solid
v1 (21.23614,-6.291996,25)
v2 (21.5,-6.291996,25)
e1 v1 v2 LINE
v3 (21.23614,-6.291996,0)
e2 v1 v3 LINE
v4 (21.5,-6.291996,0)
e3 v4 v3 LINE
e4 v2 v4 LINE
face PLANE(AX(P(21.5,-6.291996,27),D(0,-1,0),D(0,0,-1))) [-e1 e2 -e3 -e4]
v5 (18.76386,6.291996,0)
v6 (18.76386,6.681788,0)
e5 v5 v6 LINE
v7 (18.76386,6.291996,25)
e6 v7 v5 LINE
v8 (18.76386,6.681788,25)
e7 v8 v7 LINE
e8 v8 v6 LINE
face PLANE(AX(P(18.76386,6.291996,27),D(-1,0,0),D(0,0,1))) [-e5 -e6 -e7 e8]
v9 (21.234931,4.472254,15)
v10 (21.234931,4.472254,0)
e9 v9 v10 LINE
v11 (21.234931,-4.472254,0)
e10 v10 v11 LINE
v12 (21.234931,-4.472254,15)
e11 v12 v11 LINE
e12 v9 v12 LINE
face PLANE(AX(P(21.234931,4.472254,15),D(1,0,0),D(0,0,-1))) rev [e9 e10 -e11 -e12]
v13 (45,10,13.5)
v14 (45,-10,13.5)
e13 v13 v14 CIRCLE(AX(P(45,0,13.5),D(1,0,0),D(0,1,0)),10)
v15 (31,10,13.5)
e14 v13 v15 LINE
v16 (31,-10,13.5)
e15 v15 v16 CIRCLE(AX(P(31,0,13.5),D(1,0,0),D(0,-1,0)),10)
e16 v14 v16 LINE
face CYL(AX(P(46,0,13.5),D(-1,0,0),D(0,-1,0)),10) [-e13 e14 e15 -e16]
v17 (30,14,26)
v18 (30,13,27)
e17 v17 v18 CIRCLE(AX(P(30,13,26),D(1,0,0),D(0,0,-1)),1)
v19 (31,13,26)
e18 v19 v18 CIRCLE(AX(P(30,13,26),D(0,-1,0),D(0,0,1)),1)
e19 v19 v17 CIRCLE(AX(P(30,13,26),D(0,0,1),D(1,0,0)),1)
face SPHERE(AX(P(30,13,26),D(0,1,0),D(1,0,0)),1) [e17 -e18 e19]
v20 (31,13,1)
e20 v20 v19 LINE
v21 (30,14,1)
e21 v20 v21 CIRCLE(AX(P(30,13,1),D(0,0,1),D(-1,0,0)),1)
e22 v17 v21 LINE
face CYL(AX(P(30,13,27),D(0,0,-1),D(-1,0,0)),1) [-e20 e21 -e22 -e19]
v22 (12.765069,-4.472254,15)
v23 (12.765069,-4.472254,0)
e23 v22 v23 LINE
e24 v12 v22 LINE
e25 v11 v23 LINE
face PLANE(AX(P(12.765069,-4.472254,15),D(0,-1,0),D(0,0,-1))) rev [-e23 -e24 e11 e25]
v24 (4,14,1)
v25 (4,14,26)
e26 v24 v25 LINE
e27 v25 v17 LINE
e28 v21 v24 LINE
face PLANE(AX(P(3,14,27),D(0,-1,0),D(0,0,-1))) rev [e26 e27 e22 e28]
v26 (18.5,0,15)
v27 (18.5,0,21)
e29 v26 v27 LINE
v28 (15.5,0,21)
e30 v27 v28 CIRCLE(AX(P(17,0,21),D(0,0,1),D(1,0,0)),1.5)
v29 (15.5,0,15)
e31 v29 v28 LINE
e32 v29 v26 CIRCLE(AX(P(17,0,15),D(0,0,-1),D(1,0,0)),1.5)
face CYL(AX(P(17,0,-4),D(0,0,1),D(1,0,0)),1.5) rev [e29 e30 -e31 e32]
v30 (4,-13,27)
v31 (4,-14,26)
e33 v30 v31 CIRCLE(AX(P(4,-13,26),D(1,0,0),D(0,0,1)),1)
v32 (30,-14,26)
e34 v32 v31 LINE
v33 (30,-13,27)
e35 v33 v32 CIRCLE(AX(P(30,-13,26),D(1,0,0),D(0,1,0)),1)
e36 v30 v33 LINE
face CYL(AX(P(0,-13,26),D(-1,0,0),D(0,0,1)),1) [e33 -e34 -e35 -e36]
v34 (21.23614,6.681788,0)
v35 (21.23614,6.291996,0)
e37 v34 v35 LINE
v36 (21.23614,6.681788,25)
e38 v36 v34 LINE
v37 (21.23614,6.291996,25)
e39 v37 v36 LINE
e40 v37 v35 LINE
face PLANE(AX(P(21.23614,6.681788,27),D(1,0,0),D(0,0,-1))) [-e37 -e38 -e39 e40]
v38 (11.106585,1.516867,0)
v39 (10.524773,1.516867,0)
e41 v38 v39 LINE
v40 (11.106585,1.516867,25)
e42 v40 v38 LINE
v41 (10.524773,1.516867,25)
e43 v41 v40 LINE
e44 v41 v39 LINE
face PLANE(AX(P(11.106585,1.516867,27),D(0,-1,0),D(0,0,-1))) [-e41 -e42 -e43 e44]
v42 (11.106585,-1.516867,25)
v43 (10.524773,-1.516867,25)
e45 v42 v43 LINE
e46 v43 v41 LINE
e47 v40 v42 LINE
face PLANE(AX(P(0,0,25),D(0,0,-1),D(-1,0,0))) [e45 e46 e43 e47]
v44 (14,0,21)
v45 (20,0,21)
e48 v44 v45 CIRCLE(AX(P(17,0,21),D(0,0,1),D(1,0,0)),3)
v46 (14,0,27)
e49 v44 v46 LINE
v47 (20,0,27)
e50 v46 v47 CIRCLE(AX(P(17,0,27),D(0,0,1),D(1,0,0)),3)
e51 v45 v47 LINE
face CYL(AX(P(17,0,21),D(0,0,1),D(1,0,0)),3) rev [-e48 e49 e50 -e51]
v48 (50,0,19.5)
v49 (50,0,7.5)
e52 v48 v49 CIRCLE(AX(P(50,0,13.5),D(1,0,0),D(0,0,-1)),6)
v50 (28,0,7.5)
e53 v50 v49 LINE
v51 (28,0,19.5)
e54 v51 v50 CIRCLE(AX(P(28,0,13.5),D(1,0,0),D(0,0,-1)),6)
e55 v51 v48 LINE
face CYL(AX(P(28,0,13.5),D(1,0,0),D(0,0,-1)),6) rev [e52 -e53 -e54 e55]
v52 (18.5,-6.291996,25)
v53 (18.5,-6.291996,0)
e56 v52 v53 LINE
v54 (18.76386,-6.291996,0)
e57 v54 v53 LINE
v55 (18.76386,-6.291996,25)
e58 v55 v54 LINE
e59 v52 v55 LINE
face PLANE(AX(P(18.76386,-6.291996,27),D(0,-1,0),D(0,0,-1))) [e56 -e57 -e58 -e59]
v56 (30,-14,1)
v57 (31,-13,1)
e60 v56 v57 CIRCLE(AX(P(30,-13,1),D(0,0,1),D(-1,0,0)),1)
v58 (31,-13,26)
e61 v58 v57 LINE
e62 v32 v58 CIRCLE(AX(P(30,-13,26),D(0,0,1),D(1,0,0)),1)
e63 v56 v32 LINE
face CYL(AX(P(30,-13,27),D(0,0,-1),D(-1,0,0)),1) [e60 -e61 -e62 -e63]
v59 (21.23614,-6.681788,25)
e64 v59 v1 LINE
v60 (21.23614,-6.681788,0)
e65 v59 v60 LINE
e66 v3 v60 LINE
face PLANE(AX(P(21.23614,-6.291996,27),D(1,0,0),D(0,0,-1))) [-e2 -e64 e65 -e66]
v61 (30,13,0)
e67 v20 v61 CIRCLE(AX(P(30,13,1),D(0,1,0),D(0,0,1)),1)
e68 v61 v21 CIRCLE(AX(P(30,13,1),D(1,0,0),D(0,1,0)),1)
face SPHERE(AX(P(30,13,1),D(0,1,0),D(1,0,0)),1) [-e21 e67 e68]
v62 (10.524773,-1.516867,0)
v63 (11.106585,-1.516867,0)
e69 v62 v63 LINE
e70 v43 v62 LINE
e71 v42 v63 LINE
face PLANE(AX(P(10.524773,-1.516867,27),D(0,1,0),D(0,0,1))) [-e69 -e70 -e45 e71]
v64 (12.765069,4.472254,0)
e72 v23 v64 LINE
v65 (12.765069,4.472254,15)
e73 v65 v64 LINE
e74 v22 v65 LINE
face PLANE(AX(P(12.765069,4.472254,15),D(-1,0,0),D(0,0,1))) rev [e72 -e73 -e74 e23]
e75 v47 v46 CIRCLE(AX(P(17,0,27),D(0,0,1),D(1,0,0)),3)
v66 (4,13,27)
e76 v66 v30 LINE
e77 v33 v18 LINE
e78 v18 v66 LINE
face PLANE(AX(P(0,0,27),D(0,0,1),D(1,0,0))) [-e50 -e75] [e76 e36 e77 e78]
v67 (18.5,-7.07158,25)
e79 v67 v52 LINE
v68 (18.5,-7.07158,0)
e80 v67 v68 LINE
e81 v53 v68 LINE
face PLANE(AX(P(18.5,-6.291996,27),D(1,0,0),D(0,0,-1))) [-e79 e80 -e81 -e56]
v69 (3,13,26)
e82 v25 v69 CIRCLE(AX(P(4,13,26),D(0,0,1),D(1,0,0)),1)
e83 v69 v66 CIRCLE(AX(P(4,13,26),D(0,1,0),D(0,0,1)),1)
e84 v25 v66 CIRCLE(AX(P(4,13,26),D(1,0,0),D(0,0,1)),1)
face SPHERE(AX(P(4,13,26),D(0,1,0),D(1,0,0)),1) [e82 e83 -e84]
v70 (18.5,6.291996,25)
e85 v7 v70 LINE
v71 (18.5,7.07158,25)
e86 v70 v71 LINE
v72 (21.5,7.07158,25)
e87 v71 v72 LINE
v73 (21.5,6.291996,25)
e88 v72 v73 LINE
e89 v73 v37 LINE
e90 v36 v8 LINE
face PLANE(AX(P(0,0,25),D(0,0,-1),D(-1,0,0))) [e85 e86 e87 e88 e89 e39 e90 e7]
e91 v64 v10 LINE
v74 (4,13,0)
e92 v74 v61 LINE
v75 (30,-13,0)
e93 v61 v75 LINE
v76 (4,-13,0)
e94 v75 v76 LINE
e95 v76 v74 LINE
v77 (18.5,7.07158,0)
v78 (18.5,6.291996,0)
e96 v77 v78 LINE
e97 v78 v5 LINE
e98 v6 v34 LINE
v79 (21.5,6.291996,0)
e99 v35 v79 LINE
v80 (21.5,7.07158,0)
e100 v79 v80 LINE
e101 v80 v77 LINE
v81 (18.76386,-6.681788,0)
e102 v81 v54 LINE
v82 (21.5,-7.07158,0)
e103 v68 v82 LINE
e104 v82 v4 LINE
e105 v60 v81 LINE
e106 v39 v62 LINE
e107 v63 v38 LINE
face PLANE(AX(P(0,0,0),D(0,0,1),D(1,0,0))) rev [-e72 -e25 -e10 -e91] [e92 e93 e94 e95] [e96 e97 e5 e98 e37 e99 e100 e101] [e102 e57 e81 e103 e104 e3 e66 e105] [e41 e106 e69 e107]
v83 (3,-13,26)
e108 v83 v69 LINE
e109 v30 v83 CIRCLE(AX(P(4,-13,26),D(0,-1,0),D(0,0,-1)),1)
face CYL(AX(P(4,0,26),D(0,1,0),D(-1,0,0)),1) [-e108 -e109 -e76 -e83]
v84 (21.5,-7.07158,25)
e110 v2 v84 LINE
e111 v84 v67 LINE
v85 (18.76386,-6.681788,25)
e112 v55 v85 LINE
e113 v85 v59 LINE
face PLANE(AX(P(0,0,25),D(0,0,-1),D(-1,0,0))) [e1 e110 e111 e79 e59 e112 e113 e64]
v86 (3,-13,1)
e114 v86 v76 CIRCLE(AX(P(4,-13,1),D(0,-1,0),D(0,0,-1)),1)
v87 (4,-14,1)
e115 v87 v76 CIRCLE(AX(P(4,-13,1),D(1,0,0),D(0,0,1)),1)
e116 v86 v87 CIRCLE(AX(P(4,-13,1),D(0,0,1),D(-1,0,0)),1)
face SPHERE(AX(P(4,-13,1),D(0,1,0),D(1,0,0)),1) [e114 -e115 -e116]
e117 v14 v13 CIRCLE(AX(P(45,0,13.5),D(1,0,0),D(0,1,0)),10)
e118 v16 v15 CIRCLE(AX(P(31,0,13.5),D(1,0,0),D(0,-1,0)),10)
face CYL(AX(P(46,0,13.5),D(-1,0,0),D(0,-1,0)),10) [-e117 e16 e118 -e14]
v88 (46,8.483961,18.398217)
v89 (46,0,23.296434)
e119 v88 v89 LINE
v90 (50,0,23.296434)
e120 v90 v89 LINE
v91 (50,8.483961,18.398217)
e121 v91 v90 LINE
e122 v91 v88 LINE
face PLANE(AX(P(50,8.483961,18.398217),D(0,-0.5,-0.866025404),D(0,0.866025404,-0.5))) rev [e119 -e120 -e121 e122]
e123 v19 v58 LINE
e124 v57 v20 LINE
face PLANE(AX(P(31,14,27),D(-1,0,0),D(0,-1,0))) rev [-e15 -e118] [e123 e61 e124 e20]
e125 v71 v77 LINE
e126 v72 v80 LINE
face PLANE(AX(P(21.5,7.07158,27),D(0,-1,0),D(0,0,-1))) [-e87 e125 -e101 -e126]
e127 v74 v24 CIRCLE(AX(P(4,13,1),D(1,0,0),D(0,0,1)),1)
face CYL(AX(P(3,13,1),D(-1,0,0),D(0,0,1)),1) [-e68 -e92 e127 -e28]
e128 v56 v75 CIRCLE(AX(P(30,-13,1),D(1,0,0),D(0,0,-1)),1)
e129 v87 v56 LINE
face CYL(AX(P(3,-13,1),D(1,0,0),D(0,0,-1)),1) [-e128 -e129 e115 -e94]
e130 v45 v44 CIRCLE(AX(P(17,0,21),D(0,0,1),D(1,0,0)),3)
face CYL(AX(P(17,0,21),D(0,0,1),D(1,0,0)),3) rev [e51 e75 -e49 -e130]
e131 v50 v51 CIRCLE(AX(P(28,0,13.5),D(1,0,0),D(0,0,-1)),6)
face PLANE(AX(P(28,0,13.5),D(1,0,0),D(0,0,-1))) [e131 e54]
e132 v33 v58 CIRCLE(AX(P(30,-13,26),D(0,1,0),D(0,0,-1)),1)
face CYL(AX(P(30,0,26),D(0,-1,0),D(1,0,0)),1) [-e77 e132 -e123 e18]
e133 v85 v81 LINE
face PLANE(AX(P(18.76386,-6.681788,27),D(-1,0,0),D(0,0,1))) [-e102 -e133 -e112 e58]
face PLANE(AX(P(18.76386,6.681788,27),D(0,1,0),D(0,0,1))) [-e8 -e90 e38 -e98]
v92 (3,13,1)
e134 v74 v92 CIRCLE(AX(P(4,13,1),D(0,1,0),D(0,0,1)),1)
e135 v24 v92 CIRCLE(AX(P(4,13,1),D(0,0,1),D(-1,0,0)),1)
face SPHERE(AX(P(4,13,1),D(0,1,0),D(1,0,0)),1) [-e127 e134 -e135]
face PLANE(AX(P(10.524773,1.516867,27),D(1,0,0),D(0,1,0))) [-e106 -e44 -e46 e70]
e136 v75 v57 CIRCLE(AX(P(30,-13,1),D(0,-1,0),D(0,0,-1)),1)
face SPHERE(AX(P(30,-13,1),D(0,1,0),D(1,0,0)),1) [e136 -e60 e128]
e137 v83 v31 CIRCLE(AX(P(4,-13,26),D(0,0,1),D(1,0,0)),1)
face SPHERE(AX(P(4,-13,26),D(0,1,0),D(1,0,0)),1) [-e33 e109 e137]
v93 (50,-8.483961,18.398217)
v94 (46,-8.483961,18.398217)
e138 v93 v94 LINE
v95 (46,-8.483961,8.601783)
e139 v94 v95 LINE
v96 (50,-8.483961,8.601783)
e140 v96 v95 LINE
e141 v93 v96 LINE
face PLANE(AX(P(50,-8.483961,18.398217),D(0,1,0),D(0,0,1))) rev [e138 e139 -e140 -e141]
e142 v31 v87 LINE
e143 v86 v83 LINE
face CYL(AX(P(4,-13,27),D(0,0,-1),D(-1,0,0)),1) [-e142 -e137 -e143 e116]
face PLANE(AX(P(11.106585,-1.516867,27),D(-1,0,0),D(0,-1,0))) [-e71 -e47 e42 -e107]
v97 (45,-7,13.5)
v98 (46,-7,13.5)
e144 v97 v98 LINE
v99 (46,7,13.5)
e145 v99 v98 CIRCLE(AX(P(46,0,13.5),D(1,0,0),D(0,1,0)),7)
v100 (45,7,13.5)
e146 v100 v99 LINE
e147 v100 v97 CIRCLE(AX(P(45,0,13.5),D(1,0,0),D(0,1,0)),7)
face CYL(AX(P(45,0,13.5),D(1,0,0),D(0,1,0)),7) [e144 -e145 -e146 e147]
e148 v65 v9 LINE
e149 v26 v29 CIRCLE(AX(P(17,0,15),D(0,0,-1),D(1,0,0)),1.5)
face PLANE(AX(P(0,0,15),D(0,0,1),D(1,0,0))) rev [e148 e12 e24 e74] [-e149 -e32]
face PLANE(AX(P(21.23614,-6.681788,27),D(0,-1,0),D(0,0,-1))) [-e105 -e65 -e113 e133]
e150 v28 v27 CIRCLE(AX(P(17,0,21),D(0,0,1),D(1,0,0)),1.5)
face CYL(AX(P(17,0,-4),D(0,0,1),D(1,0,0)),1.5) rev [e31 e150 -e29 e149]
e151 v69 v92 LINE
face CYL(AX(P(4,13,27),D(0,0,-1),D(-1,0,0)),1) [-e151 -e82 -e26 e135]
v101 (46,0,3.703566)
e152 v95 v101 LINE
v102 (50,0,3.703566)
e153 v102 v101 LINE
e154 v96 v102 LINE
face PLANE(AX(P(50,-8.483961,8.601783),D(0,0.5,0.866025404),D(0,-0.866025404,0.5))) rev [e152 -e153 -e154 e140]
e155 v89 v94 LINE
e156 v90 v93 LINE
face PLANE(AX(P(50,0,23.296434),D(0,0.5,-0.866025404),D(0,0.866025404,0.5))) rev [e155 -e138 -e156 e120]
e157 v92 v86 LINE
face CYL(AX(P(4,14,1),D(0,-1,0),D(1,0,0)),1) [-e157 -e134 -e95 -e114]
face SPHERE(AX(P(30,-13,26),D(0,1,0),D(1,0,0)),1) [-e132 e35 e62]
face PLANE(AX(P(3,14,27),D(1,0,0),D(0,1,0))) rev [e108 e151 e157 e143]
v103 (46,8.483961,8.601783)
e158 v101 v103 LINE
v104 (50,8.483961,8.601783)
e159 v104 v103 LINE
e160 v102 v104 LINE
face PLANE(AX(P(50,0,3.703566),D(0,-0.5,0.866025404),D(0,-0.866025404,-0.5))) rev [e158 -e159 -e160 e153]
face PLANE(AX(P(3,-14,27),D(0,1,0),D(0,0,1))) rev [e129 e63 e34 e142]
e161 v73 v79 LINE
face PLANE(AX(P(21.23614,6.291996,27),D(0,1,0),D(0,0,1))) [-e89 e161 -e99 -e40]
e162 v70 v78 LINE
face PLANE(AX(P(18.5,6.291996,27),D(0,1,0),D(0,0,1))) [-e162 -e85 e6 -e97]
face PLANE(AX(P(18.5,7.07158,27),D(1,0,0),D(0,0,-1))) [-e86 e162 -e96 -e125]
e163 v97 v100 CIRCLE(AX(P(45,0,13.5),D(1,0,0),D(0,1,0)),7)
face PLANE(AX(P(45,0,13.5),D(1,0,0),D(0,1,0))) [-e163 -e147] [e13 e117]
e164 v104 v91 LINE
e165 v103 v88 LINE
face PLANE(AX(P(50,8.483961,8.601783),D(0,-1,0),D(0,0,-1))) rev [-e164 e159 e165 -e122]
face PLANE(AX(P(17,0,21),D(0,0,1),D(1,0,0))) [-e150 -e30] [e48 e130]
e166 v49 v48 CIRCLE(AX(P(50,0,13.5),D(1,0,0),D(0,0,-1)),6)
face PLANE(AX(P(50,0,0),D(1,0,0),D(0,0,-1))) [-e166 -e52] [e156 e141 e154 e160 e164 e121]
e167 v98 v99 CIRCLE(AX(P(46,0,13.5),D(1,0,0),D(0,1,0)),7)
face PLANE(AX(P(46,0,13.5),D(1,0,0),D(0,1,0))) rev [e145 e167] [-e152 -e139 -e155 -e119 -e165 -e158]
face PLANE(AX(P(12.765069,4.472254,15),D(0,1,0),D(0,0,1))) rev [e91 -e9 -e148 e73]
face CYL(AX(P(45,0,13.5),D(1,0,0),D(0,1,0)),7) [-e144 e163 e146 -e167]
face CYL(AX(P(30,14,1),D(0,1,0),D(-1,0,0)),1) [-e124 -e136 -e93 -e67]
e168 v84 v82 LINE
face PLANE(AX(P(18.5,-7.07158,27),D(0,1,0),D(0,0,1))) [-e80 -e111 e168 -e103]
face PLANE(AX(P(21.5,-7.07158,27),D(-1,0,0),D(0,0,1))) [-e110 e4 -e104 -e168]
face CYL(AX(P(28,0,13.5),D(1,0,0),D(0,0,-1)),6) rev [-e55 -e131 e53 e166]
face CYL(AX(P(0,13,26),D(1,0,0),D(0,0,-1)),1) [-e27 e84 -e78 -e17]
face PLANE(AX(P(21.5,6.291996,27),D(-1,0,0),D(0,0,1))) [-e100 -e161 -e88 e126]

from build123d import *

# Parameters (mm, degrees)
SKETCH1_W           = 28
SKETCH1_H           = 28
SKETCH1_W_2         = 0.581812165
SKETCH1_H_2         = 3.033734858
BOSS_EXTRUDE1_DEPTH = 27
SKETCH2_W           = 28
SKETCH2_H           = 28
BOSS_EXTRUDE2_DEPTH = 2
SKETCH3_R           = 3
CUT_EXTRUDE1_DEPTH  = 6
SKETCH4_R           = 1.5
CUT_EXTRUDE2_DEPTH  = 25
FILLET1_R           = 1
SKETCH5_R           = 10
SKETCH5_R_2         = 5
EXTRUDE_THIN1_DEPTH = 15
BOSS_EXTRUDE3_DEPTH = 4
CUT_EXTRUDE3_START  = -1
SKETCH7_R           = 10
SKETCH7_R_2         = 7
CUT_EXTRUDE3_DEPTH  = 1
SKETCH8_R           = 6
CUT_EXTRUDE4_DEPTH  = 22
SKETCH9_W           = 8.469861182
SKETCH9_H           = 8.944508274
CUT_EXTRUDE5_DEPTH  = 15


with BuildPart() as part:
    # Sketch1 → Boss-Extrude1 (new body)
    with BuildSketch(Plane.XY):
        with Locations((17, 0)):
            Rectangle(SKETCH1_W, SKETCH1_H)
        Polygon((18.5, 7.071580399), (18.5, 6.29199588), (18.76385967, 6.29199588), (18.76385967, 6.681788139), (21.23614033, 6.681788139), (21.23614033, 6.29199588), (21.5, 6.29199588), (21.5, 7.071580399), align=None, mode=Mode.SUBTRACT)
        with Locations((10.815679405, 0)):
            Rectangle(SKETCH1_W_2, SKETCH1_H_2, mode=Mode.SUBTRACT)
        Polygon((18.5, -6.29199588), (18.5, -7.071580399), (21.5, -7.071580399), (21.5, -6.29199588), (21.23614033, -6.29199588), (21.23614033, -6.681788139), (18.76385967, -6.681788139), (18.76385967, -6.29199588), align=None, mode=Mode.SUBTRACT)
    extrude(amount=BOSS_EXTRUDE1_DEPTH)

    # Sketch2 → Boss-Extrude2 (add)
    with BuildSketch(Plane.XY.offset(27)):
        with Locations((17, 0)):
            Rectangle(SKETCH2_W, SKETCH2_H)
    extrude(amount=-BOSS_EXTRUDE2_DEPTH)

    # Sketch3 → Cut-Extrude1 (cut)
    with BuildSketch(Plane.XY.offset(27)):
        with Locations((17, 0)):
            Circle(SKETCH3_R)
    extrude(amount=-CUT_EXTRUDE1_DEPTH, mode=Mode.SUBTRACT)

    # Sketch4 → Cut-Extrude2 (cut)
    with BuildSketch(Plane.XY.offset(21)):
        with Locations((17, 0)):
            Circle(SKETCH4_R)
    extrude(amount=-CUT_EXTRUDE2_DEPTH, mode=Mode.SUBTRACT)

    # Fillet1
    fillet1_edges = [part.edges().sort_by_distance(p)[0] for p in [
        (3, 0, 27),
        (17, -14, 27),
        (31, 0, 27),
        (17, -14, 0),
        (3, 0, 0),
        (17, 14, 0),
        (31, 0, 0),
        (31, -14, 13.5),
        (3, -14, 13.5),
        (3, 14, 13.5),
        (31, 14, 13.5),
        (17, 14, 27),
    ]]
    fillet(fillet1_edges, radius=FILLET1_R)

    # Sketch5 → Extrude-Thin1 (add)
    with BuildSketch(Plane(origin=(31, 0, 0), x_dir=(0, 0, -1), z_dir=(1, 0, 0))):
        with Locations((-13.5, 0)):
            Circle(SKETCH5_R)
        with Locations((-13.5, 0)):
            Circle(SKETCH5_R_2, mode=Mode.SUBTRACT)
    extrude(amount=EXTRUDE_THIN1_DEPTH)

    # Sketch6 → Boss-Extrude3 (add)
    with BuildSketch(Plane(origin=(46, 0, 0), x_dir=(0, 0, -1), z_dir=(1, 0, 0))):
        Polygon((-23.296433781, 0), (-18.398216891, -8.483960521), (-8.601783109, -8.483960521), (-3.703566219, 0), (-8.601783109, 8.483960521), (-18.398216891, 8.483960521), align=None)
    extrude(amount=BOSS_EXTRUDE3_DEPTH)

    # Sketch7 → Cut-Extrude3 (cut)
    with BuildSketch(Plane(origin=(46, 0, 0), x_dir=(0, 0, -1), z_dir=(1, 0, 0)).offset(CUT_EXTRUDE3_START)):
        with Locations(Location((-13.5, 0, 0), (0, 0, 270))):
            Circle(SKETCH7_R)
        with Locations(Location((-13.5, 0, 0), (0, 0, 90))):
            Circle(SKETCH7_R_2, mode=Mode.SUBTRACT)
    extrude(amount=CUT_EXTRUDE3_DEPTH, mode=Mode.SUBTRACT)

    # Sketch8 → Cut-Extrude4 (cut)
    with BuildSketch(Plane(origin=(50, 0, 0), x_dir=(0, 0, -1), z_dir=(1, 0, 0))):
        with Locations((-13.5, 0)):
            Circle(SKETCH8_R)
    extrude(amount=-CUT_EXTRUDE4_DEPTH, mode=Mode.SUBTRACT)

    # Sketch9 → Cut-Extrude5 (cut)
    with BuildSketch(Plane(origin=(0, 0, 0), x_dir=(-1, 0, 0), z_dir=(0, 0, -1))):
        with Locations((-17, 0)):
            Rectangle(SKETCH9_W, SKETCH9_H)
    extrude(amount=-CUT_EXTRUDE5_DEPTH, mode=Mode.SUBTRACT)


solid = part.part
